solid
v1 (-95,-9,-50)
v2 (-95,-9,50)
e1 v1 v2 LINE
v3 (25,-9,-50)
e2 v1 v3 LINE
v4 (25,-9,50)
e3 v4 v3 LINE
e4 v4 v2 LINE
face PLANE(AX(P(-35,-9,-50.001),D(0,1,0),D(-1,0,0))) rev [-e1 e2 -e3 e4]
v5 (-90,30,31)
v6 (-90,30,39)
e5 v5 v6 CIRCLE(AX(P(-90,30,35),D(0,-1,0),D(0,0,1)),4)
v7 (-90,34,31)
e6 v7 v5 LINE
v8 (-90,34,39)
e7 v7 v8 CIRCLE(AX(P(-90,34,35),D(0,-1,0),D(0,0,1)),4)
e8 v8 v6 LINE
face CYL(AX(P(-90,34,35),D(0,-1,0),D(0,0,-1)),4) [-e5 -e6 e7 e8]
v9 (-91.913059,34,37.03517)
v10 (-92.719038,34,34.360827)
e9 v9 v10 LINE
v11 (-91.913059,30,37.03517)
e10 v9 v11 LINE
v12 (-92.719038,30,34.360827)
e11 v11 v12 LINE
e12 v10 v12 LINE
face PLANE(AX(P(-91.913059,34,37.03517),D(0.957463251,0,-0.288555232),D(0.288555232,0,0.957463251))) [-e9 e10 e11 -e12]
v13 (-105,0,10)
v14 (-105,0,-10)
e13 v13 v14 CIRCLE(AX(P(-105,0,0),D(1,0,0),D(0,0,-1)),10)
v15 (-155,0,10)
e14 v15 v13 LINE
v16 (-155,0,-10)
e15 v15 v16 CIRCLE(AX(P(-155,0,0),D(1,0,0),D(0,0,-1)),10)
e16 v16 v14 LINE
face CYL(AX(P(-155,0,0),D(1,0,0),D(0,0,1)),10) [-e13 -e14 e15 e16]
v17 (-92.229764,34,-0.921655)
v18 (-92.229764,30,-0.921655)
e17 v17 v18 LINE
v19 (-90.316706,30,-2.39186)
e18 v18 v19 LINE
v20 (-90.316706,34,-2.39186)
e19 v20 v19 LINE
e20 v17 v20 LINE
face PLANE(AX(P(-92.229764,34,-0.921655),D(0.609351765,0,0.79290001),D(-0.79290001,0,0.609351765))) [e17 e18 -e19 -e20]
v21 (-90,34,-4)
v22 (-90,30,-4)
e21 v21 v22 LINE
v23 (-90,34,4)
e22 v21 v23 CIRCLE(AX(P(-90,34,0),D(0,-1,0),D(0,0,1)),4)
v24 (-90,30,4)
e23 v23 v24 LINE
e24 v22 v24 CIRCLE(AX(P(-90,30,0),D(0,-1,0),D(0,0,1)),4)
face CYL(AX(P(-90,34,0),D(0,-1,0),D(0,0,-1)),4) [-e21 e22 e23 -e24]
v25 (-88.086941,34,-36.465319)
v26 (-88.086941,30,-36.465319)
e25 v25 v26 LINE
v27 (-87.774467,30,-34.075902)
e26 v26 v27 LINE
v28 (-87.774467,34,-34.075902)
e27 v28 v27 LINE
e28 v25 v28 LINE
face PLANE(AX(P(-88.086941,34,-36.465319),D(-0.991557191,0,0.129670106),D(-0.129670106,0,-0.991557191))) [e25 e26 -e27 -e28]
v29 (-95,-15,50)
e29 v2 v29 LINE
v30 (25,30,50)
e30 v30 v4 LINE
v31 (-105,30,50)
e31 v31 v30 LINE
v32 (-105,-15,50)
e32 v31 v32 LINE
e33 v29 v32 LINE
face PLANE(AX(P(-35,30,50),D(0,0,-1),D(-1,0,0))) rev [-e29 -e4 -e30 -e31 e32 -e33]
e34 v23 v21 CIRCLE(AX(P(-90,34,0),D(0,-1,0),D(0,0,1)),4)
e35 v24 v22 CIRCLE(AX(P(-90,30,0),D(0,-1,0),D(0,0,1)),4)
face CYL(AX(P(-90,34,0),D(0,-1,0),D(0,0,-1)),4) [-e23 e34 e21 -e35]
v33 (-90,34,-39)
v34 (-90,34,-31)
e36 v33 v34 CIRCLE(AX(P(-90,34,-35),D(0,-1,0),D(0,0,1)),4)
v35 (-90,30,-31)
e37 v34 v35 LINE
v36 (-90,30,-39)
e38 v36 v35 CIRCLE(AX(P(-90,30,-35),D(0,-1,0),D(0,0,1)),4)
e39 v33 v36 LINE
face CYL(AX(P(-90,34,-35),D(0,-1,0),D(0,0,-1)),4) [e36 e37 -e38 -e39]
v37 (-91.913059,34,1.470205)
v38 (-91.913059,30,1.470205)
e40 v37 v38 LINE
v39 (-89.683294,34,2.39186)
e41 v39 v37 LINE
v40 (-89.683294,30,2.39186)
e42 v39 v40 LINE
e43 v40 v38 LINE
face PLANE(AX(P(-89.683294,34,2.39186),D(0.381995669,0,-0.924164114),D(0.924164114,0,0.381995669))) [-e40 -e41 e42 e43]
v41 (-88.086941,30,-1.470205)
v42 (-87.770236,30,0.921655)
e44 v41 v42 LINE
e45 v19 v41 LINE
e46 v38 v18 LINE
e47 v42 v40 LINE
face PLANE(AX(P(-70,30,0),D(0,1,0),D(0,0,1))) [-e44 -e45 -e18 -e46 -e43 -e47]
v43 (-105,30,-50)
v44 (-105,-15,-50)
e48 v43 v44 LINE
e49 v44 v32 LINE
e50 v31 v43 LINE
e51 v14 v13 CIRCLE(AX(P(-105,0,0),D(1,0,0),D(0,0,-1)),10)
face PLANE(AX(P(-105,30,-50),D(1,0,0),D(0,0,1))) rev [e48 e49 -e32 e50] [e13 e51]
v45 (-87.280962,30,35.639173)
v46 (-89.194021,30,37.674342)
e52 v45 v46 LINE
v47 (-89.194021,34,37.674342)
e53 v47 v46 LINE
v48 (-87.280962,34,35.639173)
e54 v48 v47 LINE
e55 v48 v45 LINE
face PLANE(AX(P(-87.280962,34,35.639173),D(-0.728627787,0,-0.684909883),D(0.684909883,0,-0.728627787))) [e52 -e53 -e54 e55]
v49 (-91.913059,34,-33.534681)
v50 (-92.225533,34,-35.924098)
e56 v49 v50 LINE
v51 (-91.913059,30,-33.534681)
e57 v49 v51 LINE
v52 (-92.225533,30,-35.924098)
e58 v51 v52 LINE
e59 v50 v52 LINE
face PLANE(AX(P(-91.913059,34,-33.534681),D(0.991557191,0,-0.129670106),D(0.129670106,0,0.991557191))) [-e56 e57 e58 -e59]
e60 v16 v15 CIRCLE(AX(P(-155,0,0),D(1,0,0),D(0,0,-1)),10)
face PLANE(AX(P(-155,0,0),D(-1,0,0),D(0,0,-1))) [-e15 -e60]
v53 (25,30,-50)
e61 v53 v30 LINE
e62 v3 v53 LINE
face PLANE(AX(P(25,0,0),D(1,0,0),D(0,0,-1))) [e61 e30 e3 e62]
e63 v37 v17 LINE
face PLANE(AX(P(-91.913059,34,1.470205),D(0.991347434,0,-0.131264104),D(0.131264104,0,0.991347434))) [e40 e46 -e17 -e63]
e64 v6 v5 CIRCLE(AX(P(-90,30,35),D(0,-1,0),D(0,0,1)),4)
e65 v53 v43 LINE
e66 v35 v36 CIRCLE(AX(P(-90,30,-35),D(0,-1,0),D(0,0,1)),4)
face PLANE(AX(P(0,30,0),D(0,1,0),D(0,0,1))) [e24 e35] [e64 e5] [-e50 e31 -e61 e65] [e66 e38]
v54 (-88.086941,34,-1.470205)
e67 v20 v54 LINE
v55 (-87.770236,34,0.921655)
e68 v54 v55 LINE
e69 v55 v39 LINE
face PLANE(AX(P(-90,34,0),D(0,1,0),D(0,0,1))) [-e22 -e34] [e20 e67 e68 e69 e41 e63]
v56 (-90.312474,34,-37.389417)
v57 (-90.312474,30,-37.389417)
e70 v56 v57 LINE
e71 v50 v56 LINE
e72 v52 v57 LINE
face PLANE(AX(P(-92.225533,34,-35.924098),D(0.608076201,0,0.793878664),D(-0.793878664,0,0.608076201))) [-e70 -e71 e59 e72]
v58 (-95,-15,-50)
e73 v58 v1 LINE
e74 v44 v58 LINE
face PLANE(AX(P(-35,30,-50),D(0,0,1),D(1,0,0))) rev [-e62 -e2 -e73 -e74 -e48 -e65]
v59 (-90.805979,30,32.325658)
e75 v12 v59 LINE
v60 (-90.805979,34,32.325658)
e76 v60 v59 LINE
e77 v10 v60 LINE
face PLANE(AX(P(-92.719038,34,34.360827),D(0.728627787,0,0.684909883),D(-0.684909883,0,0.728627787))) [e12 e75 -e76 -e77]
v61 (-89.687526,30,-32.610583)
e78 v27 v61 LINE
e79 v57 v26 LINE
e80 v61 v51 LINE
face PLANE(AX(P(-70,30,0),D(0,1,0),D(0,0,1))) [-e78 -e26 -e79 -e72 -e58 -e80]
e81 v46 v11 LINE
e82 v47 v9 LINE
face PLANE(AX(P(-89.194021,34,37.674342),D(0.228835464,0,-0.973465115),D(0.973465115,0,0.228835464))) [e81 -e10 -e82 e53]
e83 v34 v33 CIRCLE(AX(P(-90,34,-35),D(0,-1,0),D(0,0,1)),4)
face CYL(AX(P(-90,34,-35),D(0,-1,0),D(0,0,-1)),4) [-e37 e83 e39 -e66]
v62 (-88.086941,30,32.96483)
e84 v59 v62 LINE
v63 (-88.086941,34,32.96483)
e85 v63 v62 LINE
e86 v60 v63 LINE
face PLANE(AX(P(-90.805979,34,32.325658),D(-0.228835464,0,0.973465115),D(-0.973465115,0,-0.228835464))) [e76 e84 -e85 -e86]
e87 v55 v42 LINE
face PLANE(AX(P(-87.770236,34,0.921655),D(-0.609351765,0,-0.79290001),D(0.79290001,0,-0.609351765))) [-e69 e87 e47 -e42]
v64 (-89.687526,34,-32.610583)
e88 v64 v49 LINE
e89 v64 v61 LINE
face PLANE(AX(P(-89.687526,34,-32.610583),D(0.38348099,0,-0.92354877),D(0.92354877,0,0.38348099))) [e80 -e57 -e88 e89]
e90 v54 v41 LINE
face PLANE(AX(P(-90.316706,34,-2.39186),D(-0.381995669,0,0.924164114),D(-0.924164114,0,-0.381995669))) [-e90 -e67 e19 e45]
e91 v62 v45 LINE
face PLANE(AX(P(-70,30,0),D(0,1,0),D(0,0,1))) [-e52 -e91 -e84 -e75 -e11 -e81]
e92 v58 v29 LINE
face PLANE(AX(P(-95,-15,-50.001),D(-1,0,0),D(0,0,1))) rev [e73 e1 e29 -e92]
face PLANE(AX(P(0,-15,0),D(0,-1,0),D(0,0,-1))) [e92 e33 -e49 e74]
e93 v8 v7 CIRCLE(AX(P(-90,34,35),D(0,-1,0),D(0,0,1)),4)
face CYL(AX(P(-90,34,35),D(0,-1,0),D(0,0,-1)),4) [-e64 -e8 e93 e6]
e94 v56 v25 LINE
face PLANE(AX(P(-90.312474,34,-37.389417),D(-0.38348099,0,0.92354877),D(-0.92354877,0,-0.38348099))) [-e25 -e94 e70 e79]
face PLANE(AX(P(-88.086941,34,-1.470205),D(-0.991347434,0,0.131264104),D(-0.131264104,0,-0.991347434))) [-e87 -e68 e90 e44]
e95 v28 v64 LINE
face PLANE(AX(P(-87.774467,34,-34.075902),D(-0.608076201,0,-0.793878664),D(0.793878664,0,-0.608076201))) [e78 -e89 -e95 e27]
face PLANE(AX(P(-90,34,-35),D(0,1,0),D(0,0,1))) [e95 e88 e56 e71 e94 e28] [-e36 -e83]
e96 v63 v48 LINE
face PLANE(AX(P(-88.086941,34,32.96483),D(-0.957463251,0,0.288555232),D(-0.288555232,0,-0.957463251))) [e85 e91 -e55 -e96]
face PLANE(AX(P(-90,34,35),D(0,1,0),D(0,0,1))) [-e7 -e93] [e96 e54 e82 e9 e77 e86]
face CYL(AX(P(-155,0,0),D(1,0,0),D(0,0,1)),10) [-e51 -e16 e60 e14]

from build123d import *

# Parameters (mm, degrees)
SKETCH1_W           = 70
SKETCH1_H           = 100
BOSS_EXTRUDE1_DEPTH = 30
SKETCH2_R           = 4
BOSS_EXTRUDE2_DEPTH = 4
SKETCH3_R           = 10
BOSS_EXTRUDE3_DEPTH = 50
SKETCH4_W           = 70
SKETCH4_H           = 100
BOSS_EXTRUDE4_DEPTH = 15
SKETCH5_W           = 134.250739562
SKETCH5_H           = 64.864054132
CUT_EXTRUDE1_DEPTH  = 130
CUT_EXTRUDE2_REACH  = 189.566
SKETCH6_W           = 60
SKETCH6_H           = 6
SKETCH7_W           = 100
SKETCH7_H           = 39
BOSS_EXTRUDE5_DEPTH = 60


with BuildPart() as part:
    # Sketch1 → Boss-Extrude1 (new body)
    with BuildSketch(Plane(origin=(0, 0, 0), x_dir=(1, 0, 0), z_dir=(0, 1, 0))):
        Rectangle(SKETCH1_W, SKETCH1_H)
    extrude(amount=BOSS_EXTRUDE1_DEPTH)

    # Sketch2 → Boss-Extrude2 (add)
    # profile 1 of 3: a face of its own
    with BuildSketch(Plane(origin=(0, 30, 0), x_dir=(1, 0, 0), z_dir=(0, 1, 0))):
        with Locations(Location((20, -35, 0), (0, 0, 270))):
            Circle(SKETCH2_R)
        Polygon((21.913058762, -37.035169602), (22.719037957, -34.360827314), (20.805979195, -32.325657712), (18.086941238, -32.964830398), (17.280962043, -35.639172686), (19.194020805, -37.674342288), align=None, mode=Mode.SUBTRACT)
    # profile 2 of 3: a face of its own
    with BuildSketch(Plane(origin=(0, 30, 0), x_dir=(1, 0, 0), z_dir=(0, 1, 0))):
        with Locations(Location((20, 0, 0), (0, 0, 270))):
            Circle(SKETCH2_R)
        Polygon((21.913058762, -1.47020522), (22.229764451, 0.921654877), (20.316705689, 2.391860097), (18.086941238, 1.47020522), (17.770235549, -0.921654877), (19.683294311, -2.391860097), align=None, mode=Mode.SUBTRACT)
    # profile 3 of 3: a face of its own
    with BuildSketch(Plane(origin=(0, 30, 0), x_dir=(1, 0, 0), z_dir=(0, 1, 0))):
        with Locations(Location((20, 35, 0), (0, 0, 270))):
            Circle(SKETCH2_R)
        Polygon((21.913058762, 33.534680981), (22.225532876, 35.924097978), (20.312474114, 37.389416996), (18.086941238, 36.465319019), (17.774467124, 34.075902022), (19.687525886, 32.610583004), align=None, mode=Mode.SUBTRACT)
    extrude(amount=BOSS_EXTRUDE2_DEPTH)

    # Sketch3 → Boss-Extrude3 (add)
    with BuildSketch(Plane(origin=(35, 0, 0), x_dir=(0, 0, -1), z_dir=(1, 0, 0))):
        Circle(SKETCH3_R)
    extrude(amount=BOSS_EXTRUDE3_DEPTH)

    # Sketch4 → Boss-Extrude4 (add)
    with BuildSketch(Plane.XZ):
        Rectangle(SKETCH4_W, SKETCH4_H)
    extrude(amount=BOSS_EXTRUDE4_DEPTH)

    # Mirror1: part across plane


with BuildPart() as part_1:
    add(part.part)
    add(part.part.mirror(Plane(origin=(-35, 30, -50), x_dir=(0, 0, 1), z_dir=(1, 0, 0))))

    # Sketch5 → Cut-Extrude1 (cut)
    with BuildSketch(Plane.ZY.offset(35)):
        with Locations((0.773607985, 10.636315649)):
            Rectangle(SKETCH5_W, SKETCH5_H)
    extrude(amount=-CUT_EXTRUDE1_DEPTH, mode=Mode.SUBTRACT)

    # Sketch6 → Cut-Extrude2 (cut, up to next)
    with BuildSketch(Plane.XY.offset(50), mode=Mode.PRIVATE) as cut_extrude2_sk1:
        with Locations((-65, -12)):
            Rectangle(SKETCH6_W, SKETCH6_H)
    cut_extrude2_tool1 = extrude(cut_extrude2_sk1.sketch, amount=-CUT_EXTRUDE2_REACH, mode=Mode.PRIVATE) & part_1.part
    add(cut_extrude2_tool1.solids().sort_by_distance((-65, -12, 50))[0], mode=Mode.SUBTRACT)

    # Sketch7 → Boss-Extrude5 (add)
    with BuildSketch(Plane(origin=(-35, 0, 0), x_dir=(0, 0, -1), z_dir=(1, 0, 0))):
        with Locations((0, 10.5)):
            Rectangle(SKETCH7_W, SKETCH7_H)
    extrude(amount=BOSS_EXTRUDE5_DEPTH)


solid = part_1.part
